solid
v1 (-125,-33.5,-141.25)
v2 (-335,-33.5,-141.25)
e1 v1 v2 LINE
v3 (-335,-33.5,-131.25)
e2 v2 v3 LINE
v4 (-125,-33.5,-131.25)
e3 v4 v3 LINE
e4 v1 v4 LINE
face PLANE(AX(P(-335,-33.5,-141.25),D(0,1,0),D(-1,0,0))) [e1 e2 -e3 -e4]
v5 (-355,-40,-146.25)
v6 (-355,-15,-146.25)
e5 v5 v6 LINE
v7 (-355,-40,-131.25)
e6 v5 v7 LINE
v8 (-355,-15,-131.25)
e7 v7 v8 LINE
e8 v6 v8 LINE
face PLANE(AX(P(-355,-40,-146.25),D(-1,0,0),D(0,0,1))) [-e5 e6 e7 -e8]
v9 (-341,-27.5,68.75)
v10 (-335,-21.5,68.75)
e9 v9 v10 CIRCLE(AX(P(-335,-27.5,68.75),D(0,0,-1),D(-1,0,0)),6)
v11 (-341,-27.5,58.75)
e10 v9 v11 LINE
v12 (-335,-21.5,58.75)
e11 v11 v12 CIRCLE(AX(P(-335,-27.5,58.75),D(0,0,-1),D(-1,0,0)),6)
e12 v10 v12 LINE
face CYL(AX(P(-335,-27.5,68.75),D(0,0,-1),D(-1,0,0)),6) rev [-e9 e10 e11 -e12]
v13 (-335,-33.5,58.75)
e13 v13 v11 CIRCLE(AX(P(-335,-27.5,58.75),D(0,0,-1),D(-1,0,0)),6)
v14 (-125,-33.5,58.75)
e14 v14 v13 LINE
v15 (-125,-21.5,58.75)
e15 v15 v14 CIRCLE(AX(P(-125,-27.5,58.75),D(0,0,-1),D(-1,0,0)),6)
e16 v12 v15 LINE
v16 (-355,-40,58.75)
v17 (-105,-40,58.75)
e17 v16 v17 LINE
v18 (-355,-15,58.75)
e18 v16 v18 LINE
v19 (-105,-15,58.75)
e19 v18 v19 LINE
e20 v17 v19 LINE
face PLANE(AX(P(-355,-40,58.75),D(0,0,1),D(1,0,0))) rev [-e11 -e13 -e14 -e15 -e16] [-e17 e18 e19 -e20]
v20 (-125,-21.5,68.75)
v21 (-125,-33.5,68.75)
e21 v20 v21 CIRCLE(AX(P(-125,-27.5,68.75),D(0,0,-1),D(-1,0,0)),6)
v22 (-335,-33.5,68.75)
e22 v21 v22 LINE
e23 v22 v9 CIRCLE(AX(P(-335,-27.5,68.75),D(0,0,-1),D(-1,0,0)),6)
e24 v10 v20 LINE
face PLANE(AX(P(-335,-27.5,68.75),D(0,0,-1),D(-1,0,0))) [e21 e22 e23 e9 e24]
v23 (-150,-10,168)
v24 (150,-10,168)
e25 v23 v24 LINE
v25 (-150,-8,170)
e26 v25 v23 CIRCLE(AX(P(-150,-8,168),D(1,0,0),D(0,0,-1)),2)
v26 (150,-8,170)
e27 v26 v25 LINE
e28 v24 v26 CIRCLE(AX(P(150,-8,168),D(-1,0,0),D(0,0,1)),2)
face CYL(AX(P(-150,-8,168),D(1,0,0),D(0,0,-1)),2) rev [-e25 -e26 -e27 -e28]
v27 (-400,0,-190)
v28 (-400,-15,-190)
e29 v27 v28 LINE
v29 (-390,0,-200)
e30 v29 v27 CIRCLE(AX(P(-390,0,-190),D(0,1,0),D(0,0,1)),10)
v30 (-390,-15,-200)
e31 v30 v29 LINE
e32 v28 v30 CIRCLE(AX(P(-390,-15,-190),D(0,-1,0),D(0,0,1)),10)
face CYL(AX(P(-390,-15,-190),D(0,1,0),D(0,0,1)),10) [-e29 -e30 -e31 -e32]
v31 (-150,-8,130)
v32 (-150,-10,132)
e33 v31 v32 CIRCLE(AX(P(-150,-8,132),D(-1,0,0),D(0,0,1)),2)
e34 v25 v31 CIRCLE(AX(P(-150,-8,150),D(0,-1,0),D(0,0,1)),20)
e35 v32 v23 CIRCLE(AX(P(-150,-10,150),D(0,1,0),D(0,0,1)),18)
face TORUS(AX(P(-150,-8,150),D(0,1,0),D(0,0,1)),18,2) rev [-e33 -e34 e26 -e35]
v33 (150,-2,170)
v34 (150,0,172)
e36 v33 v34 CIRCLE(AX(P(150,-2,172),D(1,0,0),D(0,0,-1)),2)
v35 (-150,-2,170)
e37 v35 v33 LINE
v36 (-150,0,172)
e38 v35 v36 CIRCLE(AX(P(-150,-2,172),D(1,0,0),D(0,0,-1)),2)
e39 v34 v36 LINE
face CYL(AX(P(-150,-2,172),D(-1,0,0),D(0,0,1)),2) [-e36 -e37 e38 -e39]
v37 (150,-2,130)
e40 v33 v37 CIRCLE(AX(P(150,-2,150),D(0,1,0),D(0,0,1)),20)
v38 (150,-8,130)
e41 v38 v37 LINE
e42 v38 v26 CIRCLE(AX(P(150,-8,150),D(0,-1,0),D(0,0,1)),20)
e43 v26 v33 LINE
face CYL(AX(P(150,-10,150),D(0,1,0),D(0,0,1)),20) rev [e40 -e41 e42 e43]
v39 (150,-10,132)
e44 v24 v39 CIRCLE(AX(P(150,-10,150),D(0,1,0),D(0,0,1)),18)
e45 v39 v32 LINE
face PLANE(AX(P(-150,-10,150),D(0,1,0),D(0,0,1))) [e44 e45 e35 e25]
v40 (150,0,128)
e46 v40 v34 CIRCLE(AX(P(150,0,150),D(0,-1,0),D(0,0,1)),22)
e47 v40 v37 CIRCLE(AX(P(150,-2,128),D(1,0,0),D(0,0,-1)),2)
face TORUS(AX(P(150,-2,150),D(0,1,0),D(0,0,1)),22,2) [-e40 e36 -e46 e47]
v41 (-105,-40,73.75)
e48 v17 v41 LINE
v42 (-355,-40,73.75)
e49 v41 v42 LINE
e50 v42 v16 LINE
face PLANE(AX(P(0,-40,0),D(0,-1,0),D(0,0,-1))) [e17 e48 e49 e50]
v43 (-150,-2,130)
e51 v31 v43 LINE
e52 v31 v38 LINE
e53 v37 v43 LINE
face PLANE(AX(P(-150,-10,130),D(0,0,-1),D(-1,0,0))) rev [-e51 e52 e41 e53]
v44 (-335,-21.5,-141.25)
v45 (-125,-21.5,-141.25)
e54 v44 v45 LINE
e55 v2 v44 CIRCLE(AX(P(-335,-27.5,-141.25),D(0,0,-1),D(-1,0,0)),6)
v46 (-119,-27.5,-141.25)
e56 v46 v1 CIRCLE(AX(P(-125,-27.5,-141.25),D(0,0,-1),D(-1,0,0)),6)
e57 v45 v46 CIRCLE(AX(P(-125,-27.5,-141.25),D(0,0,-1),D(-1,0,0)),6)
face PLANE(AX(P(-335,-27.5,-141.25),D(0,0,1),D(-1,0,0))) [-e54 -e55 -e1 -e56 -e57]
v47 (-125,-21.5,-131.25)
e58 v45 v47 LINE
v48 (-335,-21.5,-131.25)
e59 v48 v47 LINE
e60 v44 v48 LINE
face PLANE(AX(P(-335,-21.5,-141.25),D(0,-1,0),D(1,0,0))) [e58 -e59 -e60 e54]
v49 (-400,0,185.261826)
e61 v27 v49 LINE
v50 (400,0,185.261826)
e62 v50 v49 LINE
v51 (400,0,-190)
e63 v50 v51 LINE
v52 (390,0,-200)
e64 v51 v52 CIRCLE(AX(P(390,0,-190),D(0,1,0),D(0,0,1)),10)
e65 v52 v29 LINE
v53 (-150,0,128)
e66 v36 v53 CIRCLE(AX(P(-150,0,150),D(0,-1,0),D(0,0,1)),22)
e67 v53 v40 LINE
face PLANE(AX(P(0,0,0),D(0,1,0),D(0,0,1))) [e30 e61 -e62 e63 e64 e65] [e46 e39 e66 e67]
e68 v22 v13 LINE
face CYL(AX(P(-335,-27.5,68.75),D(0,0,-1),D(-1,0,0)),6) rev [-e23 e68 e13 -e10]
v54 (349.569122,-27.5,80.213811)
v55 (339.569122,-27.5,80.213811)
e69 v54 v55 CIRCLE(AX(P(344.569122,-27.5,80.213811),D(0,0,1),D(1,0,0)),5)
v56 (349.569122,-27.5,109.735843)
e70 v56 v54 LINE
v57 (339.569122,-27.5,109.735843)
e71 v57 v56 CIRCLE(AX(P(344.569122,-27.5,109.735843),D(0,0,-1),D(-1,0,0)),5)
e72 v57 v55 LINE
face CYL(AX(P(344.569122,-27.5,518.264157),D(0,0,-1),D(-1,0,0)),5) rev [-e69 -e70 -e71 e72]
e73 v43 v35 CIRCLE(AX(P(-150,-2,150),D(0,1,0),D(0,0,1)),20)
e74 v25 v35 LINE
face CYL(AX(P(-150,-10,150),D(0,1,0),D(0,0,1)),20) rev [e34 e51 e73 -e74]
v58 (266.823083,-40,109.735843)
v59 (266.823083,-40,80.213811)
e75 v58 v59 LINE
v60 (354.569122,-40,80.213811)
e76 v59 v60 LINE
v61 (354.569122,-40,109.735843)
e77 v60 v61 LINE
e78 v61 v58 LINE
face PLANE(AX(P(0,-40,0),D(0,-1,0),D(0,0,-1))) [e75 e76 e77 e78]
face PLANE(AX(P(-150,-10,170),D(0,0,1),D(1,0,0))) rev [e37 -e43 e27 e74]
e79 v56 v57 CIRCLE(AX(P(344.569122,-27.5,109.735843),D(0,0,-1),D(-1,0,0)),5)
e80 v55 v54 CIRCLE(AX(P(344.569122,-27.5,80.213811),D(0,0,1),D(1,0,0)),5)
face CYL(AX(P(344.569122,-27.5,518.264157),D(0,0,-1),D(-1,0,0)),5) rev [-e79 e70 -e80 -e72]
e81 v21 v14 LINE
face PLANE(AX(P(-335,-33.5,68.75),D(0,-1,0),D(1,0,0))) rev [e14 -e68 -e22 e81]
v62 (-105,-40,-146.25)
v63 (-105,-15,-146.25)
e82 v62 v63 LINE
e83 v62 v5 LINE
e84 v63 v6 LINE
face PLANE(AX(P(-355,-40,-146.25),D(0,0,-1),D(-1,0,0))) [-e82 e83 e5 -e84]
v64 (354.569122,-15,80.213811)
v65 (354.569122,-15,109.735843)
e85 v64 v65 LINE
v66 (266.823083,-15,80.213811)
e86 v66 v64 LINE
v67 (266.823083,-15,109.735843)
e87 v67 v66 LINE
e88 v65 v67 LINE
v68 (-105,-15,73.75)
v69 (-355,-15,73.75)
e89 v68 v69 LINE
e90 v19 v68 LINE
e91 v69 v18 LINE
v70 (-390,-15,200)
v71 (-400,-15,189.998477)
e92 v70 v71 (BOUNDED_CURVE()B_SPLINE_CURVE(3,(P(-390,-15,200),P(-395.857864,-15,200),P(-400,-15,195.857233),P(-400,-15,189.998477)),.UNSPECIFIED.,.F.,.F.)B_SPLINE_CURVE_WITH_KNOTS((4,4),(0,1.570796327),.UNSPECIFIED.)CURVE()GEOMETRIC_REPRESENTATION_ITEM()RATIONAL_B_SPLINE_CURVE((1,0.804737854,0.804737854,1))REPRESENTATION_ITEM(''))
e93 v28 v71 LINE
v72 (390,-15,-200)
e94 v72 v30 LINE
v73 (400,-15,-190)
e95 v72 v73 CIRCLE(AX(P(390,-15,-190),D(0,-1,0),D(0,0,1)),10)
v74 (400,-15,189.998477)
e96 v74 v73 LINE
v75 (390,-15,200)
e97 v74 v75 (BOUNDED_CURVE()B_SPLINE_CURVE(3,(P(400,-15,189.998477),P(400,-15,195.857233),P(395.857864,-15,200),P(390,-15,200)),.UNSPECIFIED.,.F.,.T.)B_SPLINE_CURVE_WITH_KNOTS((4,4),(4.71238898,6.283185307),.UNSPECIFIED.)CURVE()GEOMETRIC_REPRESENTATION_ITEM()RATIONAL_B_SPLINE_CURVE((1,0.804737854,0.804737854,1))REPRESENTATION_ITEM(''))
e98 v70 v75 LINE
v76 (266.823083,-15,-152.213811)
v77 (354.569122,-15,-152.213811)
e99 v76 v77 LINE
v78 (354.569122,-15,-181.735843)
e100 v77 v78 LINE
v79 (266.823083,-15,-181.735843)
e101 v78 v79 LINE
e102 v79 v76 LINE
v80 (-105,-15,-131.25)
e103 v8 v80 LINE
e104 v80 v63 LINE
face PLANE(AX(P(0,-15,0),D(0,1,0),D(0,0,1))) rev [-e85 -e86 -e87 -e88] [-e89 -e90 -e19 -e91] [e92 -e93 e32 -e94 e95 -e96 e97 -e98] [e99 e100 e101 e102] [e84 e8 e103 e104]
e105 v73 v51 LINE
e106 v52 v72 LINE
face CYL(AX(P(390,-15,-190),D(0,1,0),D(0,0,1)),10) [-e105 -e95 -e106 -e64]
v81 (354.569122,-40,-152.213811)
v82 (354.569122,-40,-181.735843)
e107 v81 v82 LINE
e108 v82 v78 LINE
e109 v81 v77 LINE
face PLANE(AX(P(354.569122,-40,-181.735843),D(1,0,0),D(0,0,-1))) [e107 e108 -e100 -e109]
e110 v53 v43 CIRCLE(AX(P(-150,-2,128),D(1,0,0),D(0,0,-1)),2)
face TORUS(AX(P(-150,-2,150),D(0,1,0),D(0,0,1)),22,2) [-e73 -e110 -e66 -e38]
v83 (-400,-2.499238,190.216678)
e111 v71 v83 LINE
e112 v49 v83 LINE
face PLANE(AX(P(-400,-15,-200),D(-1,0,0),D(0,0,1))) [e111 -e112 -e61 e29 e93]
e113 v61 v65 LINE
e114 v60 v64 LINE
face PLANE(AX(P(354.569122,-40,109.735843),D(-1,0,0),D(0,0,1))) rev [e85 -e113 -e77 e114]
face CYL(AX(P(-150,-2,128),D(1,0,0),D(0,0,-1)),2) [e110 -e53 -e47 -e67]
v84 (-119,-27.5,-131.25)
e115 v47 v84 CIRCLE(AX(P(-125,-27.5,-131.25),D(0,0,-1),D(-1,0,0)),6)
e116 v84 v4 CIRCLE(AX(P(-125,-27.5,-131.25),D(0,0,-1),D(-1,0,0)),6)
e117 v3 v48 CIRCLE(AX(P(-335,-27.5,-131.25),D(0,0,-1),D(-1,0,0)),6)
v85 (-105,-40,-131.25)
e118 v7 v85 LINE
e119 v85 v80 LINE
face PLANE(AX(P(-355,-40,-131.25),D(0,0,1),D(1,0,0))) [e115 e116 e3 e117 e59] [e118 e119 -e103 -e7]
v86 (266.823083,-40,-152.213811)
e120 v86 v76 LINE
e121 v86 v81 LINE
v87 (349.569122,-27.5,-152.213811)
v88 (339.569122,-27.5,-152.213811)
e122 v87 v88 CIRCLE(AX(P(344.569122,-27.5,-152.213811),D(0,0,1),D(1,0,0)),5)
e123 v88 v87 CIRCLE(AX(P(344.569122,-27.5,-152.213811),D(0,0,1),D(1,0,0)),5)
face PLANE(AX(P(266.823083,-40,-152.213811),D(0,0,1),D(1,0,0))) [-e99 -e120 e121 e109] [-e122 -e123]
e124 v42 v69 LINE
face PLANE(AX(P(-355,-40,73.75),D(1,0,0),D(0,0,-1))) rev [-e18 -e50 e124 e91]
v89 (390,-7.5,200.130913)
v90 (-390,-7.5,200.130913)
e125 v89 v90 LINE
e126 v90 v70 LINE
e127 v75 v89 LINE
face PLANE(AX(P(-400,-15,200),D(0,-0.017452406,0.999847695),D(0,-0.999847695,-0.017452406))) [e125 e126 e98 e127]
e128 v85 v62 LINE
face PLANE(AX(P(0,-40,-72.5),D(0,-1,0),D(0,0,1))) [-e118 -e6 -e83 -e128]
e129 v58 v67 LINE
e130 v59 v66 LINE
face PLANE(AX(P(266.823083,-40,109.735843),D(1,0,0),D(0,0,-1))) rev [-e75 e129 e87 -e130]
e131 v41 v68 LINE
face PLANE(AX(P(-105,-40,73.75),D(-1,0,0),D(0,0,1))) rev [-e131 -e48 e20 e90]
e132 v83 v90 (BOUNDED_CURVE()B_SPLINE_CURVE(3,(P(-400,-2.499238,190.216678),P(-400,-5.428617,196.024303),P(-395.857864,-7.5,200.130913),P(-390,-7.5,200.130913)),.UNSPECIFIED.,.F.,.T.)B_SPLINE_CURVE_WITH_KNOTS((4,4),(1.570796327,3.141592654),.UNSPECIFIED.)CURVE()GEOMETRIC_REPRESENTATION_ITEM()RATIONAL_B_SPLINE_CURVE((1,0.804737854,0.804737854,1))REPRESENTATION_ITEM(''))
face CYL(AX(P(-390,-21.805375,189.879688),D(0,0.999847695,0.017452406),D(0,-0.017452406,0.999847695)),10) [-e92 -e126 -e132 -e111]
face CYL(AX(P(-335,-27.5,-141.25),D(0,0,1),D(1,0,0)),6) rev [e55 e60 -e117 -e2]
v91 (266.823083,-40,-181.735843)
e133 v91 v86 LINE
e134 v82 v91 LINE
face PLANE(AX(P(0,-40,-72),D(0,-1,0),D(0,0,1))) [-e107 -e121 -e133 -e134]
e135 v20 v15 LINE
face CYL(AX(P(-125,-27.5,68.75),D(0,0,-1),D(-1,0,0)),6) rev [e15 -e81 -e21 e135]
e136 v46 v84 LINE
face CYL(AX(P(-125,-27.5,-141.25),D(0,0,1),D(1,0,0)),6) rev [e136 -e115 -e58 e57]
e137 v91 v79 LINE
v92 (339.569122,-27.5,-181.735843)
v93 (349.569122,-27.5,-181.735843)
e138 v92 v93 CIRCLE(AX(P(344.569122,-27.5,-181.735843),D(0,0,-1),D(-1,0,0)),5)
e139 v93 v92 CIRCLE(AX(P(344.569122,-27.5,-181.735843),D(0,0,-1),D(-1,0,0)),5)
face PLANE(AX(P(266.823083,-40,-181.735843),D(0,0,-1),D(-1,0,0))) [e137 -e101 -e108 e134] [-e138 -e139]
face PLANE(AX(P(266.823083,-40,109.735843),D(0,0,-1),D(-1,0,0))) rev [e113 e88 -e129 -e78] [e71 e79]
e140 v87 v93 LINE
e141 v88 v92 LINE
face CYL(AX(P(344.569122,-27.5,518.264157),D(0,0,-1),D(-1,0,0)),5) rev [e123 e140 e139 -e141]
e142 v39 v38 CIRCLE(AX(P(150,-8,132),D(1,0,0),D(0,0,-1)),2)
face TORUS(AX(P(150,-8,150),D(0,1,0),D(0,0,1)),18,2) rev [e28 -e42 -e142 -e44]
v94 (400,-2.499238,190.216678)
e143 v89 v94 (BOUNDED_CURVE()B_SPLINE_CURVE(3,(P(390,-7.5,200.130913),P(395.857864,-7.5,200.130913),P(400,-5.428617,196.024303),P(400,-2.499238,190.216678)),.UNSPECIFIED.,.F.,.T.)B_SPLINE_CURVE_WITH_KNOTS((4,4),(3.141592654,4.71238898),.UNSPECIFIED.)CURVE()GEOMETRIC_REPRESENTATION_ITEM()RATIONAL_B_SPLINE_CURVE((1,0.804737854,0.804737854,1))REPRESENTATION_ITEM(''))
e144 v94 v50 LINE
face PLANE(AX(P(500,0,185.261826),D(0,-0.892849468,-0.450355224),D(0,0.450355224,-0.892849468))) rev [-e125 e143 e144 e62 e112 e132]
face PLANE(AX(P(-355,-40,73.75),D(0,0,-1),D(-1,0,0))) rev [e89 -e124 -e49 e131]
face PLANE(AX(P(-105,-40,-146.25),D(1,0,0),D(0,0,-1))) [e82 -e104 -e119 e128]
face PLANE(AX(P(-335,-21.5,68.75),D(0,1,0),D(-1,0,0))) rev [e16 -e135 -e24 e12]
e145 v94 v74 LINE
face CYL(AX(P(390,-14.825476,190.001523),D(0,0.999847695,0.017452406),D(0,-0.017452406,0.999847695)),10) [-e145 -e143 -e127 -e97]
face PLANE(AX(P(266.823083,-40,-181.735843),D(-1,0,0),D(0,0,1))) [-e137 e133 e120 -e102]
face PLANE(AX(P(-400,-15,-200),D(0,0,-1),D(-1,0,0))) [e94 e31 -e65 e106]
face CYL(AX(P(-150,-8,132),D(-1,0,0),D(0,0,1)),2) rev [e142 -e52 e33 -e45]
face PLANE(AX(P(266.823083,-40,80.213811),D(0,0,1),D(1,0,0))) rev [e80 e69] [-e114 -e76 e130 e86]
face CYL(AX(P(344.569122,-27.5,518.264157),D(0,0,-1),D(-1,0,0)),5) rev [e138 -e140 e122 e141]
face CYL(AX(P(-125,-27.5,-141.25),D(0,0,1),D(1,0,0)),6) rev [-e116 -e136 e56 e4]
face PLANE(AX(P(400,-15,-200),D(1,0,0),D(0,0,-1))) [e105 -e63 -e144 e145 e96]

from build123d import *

# Parameters (mm, degrees)
SKETCH1_W           = 800
SKETCH1_H           = 400
BOSS_EXTRUDE1_DEPTH = 15
DRAFT1_ANGLE        = 1
FILLET1_R           = 10
CUT_EXTRUDE1_DEPTH  = 900
CUT_EXTRUDE2_DEPTH  = 10
FILLET2_R           = 2
SKETCH4_W           = 250
SKETCH4_H           = 15
BOSS_EXTRUDE2_DEPTH = 25
CUT_EXTRUDE4_DEPTH  = 10
SKETCH8_W           = 87.746039113
SKETCH8_H           = 29.522031851
BOSS_EXTRUDE3_DEPTH = 25
SKETCH9_R           = 5
CUT_EXTRUDE5_DEPTH  = 700


with BuildPart() as part:
    # Sketch1 → Boss-Extrude1 (new body)
    with BuildSketch(Plane(origin=(0, 0, 0), x_dir=(1, 0, 0), z_dir=(0, 1, 0))):
        Rectangle(SKETCH1_W, SKETCH1_H)
    extrude(amount=-BOSS_EXTRUDE1_DEPTH)

    # Draft1
    draft1_faces = [part.faces().sort_by_distance(p)[0] for p in [
        (0, -7.5, 200),
    ]]
    draft(draft1_faces, Plane(origin=(0, -15, 0), x_dir=(0, 0, -1), z_dir=(0, -1, 0)), DRAFT1_ANGLE)

    # Fillet1
    fillet1_edges = [part.edges().sort_by_distance(p)[0] for p in [
        (400, -7.5, 200.130912987),
        (-400, -7.5, 200.130912987),
        (-400, -7.5, -200),
        (400, -7.5, -200),
    ]]
    fillet(fillet1_edges, radius=FILLET1_R)

    # Sketch2 → Cut-Extrude1 (cut)
    with BuildSketch(Plane.ZY.offset(400)):
        Polygon((185.261825974, 0), (200.130912987, -7.5), (200.261825974, 0), align=None)
    extrude(amount=-CUT_EXTRUDE1_DEPTH, mode=Mode.SUBTRACT)

    # Sketch3 → Cut-Extrude2 (cut)
    with BuildSketch(Plane(origin=(0, 0, 0), x_dir=(1, 0, 0), z_dir=(0, 1, 0))):
        with BuildLine():
            Line((-150, -130), (150, -130))
            ThreePointArc((150, -130), (170, -150), (150, -170))
            Line((150, -170), (-150, -170))
            ThreePointArc((-150, -170), (-170, -150), (-150, -130))
        make_face()
    extrude(amount=-CUT_EXTRUDE2_DEPTH, mode=Mode.SUBTRACT)

    # Fillet2
    fillet2_edges = [part.edges().sort_by_distance(p)[0] for p in [
        (-170, -10, 150),
        (0, -10, 130),
        (170, -10, 150),
        (0, -10, 170),
        (-170, 0, 150),
        (0, 0, 170),
        (170, 0, 150),
        (0, 0, 130),
    ]]
    fillet(fillet2_edges, radius=FILLET2_R)

    # Sketch4 → Boss-Extrude2 (add)
    with BuildSketch(Plane.XZ.offset(15)):
        with Locations((-230, 66.25)):
            Rectangle(SKETCH4_W, SKETCH4_H)
    boss_extrude2 = extrude(amount=BOSS_EXTRUDE2_DEPTH)

    # Sketch7 → Cut-Extrude4 (cut)
    with BuildSketch(Plane(origin=(0, 0, 58.75), x_dir=(-1, 0, 0), z_dir=(0, 0, -1))):
        with BuildLine():
            Line((335, -33.5), (125, -33.5))
            ThreePointArc((125, -33.5), (119, -27.5), (125, -21.5))
            Line((125, -21.5), (335, -21.5))
            ThreePointArc((335, -21.5), (341, -27.5), (335, -33.5))
        make_face()
    cut_extrude4 = extrude(amount=-CUT_EXTRUDE4_DEPTH, mode=Mode.SUBTRACT)

    # Mirror2: Boss-Extrude2, Cut-Extrude4 across plane
    add(boss_extrude2.mirror(Plane.XY.offset(-36.25)))
    add(cut_extrude4.mirror(Plane.XY.offset(-36.25)), mode=Mode.SUBTRACT)

    # Sketch8 → Boss-Extrude3 (add)
    with BuildSketch(Plane.XZ.offset(15)):
        with Locations((310.696102603, 94.974826804)):
            Rectangle(SKETCH8_W, SKETCH8_H)
    boss_extrude3 = extrude(amount=BOSS_EXTRUDE3_DEPTH)

    # Mirror3: Boss-Extrude3 across plane
    add(boss_extrude3.mirror(Plane(origin=(0, 0, -36), x_dir=(1, 0, 0), z_dir=(0, 0, -1))))

    # Sketch9 → Cut-Extrude5 (cut)
    with BuildSketch(Plane(origin=(0, 0, -181.735842729), x_dir=(-1, 0, 0), z_dir=(0, 0, -1))):
        with Locations((-344.56912216, -27.5)):
            Circle(SKETCH9_R)
    extrude(amount=-CUT_EXTRUDE5_DEPTH, mode=Mode.SUBTRACT)


solid = part.part
